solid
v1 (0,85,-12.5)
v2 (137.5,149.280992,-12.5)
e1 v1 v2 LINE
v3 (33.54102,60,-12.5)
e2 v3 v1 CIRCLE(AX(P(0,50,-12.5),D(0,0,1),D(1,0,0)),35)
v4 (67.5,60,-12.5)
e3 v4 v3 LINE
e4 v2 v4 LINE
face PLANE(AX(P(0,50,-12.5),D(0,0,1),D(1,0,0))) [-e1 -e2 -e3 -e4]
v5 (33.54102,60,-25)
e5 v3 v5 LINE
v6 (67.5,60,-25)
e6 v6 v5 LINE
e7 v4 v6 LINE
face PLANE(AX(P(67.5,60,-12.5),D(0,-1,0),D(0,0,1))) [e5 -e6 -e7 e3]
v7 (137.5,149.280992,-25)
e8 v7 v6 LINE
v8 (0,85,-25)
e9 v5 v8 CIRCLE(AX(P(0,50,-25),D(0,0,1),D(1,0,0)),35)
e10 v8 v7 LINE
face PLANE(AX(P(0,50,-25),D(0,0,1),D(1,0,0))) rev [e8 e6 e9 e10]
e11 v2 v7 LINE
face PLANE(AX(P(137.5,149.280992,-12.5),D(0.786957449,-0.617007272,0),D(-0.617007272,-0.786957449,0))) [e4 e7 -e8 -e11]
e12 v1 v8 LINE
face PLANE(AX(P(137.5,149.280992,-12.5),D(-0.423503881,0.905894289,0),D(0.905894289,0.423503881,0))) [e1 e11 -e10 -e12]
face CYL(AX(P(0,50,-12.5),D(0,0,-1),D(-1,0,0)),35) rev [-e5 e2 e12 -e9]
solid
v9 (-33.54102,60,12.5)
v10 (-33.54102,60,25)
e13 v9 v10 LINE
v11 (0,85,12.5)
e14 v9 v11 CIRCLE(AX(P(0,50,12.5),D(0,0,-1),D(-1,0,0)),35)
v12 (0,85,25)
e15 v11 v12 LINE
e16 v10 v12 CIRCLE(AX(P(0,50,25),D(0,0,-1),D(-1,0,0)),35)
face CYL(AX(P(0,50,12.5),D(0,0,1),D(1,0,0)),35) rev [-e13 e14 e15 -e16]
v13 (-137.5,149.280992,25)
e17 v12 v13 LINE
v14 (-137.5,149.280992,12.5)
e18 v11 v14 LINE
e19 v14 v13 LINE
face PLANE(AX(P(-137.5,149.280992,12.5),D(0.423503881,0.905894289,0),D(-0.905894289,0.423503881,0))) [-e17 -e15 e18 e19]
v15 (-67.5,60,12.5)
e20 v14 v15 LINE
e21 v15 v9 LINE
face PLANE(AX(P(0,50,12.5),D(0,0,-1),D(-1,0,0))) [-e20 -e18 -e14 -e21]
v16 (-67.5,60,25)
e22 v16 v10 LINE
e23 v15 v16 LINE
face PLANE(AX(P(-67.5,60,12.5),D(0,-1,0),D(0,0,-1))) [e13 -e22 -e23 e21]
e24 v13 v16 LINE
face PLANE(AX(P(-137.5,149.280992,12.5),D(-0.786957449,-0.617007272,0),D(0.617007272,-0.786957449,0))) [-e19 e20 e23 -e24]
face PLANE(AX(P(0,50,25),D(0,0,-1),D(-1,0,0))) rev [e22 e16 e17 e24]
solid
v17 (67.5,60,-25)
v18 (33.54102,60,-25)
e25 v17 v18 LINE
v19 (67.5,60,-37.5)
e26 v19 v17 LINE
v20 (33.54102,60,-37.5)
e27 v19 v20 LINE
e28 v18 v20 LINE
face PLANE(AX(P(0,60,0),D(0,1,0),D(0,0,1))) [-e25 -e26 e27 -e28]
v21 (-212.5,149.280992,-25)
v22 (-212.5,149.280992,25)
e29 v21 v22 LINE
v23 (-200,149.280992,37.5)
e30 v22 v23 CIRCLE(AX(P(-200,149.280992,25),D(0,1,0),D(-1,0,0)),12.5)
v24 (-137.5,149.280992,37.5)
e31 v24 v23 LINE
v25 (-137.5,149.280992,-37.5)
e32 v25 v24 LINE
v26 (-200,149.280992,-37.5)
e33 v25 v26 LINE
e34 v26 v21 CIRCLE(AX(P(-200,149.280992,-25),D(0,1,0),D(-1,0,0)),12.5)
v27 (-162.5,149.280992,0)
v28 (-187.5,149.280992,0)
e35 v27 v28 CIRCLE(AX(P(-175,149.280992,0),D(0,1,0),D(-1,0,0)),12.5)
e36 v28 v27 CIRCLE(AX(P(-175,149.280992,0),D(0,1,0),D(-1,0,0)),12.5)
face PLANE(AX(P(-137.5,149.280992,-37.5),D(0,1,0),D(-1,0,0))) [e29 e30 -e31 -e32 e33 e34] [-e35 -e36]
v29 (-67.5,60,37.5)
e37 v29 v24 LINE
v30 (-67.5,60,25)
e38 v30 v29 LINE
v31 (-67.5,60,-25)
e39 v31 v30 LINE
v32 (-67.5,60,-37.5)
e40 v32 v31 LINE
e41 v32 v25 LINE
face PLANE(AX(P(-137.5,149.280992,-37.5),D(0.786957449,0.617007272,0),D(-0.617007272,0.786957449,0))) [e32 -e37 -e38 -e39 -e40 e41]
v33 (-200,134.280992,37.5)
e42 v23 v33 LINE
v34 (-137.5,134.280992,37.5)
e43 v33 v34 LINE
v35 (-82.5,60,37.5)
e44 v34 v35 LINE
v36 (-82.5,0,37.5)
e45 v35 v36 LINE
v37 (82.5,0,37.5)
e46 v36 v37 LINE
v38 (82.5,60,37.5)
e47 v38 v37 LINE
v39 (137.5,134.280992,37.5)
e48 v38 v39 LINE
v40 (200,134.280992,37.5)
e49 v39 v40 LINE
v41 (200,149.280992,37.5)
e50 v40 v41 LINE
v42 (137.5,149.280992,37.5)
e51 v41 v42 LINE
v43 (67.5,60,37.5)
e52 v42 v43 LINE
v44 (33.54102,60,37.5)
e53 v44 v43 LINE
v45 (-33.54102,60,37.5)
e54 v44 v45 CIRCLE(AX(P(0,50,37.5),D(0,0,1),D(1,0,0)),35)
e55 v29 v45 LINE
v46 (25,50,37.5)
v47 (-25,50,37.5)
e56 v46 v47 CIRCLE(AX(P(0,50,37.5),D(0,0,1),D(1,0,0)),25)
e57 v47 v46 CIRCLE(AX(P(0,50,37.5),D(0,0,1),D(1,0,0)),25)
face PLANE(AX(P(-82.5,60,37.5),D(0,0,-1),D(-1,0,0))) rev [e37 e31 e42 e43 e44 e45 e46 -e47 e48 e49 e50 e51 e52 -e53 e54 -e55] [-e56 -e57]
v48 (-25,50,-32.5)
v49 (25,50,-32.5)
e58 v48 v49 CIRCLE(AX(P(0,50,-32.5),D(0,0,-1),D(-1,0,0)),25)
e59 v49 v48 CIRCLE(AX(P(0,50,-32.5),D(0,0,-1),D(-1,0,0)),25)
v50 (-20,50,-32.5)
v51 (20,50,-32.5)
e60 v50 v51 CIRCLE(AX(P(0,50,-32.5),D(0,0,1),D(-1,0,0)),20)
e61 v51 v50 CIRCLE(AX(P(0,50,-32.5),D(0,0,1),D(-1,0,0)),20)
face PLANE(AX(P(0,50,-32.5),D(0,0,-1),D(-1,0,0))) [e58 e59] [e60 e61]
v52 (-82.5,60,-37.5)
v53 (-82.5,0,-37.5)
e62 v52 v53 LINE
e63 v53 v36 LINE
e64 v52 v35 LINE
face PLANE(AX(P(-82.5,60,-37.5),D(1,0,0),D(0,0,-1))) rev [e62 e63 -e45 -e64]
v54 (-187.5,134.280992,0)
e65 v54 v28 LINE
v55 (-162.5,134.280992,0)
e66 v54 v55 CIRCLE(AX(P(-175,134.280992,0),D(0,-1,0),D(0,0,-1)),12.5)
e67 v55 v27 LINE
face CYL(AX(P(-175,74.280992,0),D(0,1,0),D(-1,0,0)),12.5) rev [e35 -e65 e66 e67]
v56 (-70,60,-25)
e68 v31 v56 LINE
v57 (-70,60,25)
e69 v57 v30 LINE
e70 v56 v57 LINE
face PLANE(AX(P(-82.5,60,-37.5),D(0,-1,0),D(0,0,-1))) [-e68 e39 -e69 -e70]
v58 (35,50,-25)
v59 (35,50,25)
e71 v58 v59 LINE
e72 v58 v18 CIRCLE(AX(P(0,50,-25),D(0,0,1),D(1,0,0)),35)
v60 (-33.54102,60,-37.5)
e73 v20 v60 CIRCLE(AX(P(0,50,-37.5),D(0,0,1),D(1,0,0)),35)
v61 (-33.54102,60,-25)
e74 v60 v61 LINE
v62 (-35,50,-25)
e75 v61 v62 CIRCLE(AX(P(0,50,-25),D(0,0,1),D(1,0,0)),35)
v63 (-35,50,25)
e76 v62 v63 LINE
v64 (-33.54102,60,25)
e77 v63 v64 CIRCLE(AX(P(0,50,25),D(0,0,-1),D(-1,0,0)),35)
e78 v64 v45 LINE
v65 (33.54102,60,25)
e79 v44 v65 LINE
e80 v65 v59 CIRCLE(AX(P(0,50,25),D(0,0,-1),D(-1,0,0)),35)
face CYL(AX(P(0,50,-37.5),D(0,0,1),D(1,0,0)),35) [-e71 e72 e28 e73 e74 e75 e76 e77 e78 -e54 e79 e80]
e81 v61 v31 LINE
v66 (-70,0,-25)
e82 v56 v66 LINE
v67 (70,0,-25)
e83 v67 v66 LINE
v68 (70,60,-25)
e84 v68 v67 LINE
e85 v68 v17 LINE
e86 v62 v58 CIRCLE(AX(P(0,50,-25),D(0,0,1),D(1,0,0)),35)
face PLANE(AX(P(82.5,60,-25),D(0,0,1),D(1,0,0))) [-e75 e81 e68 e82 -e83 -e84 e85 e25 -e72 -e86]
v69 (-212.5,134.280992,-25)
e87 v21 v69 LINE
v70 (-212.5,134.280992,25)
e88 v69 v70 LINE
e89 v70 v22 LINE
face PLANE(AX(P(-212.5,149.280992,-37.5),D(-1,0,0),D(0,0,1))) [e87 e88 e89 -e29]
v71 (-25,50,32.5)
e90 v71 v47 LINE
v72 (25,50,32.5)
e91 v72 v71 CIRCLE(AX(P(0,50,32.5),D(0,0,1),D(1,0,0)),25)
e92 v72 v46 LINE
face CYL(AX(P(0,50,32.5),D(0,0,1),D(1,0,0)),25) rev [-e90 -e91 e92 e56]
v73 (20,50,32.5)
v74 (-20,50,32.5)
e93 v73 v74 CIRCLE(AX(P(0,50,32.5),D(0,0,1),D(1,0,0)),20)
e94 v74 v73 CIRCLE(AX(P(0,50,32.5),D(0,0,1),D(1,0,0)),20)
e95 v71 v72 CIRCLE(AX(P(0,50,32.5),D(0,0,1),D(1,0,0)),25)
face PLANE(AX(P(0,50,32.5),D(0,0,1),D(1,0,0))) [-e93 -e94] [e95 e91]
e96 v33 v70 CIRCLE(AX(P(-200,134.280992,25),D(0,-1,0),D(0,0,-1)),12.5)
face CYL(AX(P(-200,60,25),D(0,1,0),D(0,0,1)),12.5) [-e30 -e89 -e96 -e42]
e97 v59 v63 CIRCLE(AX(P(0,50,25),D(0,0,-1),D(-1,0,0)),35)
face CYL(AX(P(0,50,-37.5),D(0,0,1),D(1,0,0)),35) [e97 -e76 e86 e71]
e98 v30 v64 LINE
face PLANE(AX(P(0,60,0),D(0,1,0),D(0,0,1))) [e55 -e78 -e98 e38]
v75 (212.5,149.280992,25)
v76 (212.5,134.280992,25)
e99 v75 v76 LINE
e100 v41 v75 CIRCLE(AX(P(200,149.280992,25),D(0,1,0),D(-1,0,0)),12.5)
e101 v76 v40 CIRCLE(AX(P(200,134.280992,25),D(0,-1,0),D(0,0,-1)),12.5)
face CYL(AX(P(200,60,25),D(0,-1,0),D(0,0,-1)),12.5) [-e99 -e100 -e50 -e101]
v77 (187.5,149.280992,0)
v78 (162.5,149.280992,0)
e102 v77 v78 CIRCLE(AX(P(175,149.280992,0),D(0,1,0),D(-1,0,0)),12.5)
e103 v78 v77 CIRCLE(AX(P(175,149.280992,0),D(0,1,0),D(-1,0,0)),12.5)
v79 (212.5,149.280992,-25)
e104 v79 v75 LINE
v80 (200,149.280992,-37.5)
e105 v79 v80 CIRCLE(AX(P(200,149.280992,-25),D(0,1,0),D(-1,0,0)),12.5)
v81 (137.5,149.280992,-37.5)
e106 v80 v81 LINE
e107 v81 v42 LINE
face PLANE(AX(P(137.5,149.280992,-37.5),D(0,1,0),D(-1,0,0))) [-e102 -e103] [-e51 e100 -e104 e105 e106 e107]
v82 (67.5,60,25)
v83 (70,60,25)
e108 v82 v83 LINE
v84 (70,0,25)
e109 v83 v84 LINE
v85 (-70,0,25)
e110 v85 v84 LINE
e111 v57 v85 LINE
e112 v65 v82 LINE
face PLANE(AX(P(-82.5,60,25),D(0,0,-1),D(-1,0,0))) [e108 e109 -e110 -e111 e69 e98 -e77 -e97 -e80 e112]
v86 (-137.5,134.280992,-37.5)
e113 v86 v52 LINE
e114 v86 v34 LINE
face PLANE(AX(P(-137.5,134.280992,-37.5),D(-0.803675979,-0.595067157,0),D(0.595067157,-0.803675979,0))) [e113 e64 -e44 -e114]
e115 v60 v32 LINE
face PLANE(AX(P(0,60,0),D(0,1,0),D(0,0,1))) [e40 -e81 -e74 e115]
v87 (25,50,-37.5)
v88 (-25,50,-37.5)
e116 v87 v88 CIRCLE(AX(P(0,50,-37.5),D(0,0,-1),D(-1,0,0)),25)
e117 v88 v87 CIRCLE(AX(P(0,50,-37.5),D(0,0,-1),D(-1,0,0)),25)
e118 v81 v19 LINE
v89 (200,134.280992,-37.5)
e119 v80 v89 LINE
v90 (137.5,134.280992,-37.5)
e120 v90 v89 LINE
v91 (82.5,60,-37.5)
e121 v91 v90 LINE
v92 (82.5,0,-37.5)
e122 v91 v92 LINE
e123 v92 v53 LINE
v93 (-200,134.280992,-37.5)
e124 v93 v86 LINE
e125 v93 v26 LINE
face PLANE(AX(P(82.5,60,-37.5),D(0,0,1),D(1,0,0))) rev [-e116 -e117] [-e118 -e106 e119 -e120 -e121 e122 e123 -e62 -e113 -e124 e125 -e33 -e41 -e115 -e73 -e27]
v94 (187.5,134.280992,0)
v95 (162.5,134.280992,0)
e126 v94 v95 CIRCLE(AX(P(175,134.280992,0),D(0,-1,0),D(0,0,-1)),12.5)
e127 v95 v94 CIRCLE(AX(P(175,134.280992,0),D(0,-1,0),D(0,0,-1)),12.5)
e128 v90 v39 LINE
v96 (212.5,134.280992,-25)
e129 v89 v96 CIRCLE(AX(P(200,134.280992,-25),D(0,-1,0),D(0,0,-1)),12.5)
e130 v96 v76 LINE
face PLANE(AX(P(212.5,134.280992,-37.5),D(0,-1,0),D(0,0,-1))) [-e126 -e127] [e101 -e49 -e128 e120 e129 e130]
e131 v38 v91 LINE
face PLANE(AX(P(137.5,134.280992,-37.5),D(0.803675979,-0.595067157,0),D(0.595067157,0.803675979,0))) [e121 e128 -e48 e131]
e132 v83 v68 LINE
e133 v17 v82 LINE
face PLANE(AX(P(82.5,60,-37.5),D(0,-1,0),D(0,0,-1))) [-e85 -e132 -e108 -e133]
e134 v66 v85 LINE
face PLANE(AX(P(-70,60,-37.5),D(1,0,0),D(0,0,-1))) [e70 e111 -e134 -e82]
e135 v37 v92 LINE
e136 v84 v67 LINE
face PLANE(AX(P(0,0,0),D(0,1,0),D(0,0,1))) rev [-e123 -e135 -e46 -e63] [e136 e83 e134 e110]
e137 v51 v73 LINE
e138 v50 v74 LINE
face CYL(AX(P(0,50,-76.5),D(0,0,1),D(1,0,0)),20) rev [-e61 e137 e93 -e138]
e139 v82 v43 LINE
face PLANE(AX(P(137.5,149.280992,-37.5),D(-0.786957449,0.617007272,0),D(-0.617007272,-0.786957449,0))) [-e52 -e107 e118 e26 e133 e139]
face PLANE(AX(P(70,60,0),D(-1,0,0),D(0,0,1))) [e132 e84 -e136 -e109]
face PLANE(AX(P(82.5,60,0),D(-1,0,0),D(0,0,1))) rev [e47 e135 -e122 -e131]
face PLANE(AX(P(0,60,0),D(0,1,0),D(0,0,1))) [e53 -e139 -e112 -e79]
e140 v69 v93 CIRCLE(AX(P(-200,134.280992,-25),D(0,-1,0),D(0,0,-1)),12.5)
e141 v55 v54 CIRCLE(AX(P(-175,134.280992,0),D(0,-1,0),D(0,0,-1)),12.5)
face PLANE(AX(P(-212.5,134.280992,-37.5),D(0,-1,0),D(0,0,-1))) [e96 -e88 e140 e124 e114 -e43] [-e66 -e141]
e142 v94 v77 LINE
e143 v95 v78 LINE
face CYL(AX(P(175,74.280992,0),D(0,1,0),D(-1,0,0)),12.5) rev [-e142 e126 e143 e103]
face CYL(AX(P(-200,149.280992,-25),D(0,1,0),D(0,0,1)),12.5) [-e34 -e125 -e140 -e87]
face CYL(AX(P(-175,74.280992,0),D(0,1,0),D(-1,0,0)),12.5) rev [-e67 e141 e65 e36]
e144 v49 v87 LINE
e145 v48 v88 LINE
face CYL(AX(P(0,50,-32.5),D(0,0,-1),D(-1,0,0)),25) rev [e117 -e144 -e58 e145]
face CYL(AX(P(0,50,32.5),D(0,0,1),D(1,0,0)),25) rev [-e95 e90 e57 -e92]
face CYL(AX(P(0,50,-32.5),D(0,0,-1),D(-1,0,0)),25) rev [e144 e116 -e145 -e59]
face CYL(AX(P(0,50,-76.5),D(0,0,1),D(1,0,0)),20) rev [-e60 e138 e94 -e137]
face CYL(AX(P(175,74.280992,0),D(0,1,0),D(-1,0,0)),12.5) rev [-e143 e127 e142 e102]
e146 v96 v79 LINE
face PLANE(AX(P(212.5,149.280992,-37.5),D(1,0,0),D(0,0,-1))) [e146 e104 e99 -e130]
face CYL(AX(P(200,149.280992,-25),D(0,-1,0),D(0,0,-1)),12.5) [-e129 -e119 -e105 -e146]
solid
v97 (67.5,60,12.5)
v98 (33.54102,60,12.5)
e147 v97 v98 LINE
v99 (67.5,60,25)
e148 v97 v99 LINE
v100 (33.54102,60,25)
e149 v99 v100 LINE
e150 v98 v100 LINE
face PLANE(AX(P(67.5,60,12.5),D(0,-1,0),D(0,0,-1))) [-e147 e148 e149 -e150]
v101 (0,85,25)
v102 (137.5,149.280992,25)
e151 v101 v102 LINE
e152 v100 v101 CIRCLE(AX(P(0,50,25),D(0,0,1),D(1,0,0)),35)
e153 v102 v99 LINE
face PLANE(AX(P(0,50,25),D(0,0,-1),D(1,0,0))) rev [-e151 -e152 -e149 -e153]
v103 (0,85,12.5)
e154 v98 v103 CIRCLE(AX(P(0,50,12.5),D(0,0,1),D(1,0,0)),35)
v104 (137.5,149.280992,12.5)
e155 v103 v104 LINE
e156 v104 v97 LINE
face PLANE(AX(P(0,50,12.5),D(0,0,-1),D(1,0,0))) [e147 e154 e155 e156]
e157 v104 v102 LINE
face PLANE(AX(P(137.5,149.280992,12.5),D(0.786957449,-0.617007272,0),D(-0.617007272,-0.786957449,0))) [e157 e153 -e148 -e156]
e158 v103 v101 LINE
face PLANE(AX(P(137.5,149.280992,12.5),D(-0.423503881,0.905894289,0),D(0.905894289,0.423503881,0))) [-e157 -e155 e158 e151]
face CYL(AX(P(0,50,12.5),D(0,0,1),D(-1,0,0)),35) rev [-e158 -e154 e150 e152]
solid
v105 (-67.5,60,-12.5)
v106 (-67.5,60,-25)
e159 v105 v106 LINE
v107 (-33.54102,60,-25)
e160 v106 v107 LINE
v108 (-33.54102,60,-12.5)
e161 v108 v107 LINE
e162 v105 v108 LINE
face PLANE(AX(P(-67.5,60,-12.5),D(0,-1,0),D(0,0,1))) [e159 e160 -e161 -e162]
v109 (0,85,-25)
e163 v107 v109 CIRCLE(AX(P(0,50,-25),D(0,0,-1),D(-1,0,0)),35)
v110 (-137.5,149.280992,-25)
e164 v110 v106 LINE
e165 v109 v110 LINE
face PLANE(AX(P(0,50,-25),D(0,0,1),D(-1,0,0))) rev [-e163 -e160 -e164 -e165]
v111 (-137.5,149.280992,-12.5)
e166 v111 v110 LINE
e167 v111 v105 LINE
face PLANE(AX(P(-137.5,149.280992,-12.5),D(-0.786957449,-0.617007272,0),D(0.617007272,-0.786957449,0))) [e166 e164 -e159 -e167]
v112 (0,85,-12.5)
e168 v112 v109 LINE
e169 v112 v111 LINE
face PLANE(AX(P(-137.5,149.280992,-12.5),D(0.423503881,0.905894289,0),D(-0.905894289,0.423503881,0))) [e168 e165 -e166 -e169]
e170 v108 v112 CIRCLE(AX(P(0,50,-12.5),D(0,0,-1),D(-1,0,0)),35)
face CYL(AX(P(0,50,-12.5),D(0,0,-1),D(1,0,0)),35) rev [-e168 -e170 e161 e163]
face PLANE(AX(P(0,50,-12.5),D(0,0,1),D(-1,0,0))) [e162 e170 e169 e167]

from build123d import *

# Parameters (mm, degrees)
BRACKET_BODY_THIN_60X12_5_DEPTH = 60
MOUNTING_FLANGE_PADS_DEPTH      = 75
FLANGE_HOLES_SKETCH_R           = 12.5
FLANGE_MOUNTING_HOLES_2X_DEPTH  = 75
FLANGE_CORNER_FILLET_R12_5_A_R  = 12.5
FLANGE_CORNER_FILLET_R12_5_B_R  = 12.5
BEARING_BOSS_SKETCH_R           = 35
BEARING_BOSS_DEPTH              = 75
BORE_RECESS_A_SKETCH_R          = 25
BORE_RECESS_A_5MM_DEPTH         = 5
BEARING_BORE_SKETCH_R           = 20
BEARING_BORE_DEPTH              = 109
BORE_START                      = -5
BORE_RECESS_B_SKETCH_R          = 25
BORE_RECESS_B_5MM_DEPTH         = 5
RIB_DEPTH                       = 12.5


with BuildPart() as part:
    # Bracket Profile Sketch → Bracket Body Thin 60x12.5 (new body)
    with BuildSketch(Plane(origin=(0, 0, 0), x_dir=(1, 0, 0), z_dir=(0, 1, 0))):
        Polygon((82.5, 0), (82.5, 37.5), (-82.5, 37.5), (-82.5, -37.5), (82.5, -37.5), align=None)
        Polygon((70, 0), (70, 25), (-70, 25), (-70, -25), (70, -25), align=None, mode=Mode.SUBTRACT)
    extrude(amount=BRACKET_BODY_THIN_60X12_5_DEPTH)

    # Flange Pads Sketch → Mounting Flange Pads (add)
    with BuildSketch(Plane.XY.offset(37.5)):
        Polygon((82.5, 60), (67.5, 60), (137.5, 149.280992191), (212.5, 149.280992191), (212.5, 134.280992191), (137.5, 134.280992191), align=None)
        Polygon((-137.5, 149.280992191), (-67.5, 60), (-82.5, 60), (-137.5, 134.280992191), (-212.5, 134.280992191), (-212.5, 149.280992191), align=None)
    extrude(amount=-MOUNTING_FLANGE_PADS_DEPTH)

    # Flange Holes Sketch → Flange Mounting Holes 2x (cut)
    with BuildSketch(Plane(origin=(0, 149.280992191, 0), x_dir=(1, 0, 0), z_dir=(0, 1, 0))):
        with Locations(Location((175, 0, 0), (0, 0, 180))):
            Circle(FLANGE_HOLES_SKETCH_R)
        with Locations(Location((-175, 0, 0), (0, 0, 180))):
            Circle(FLANGE_HOLES_SKETCH_R)
    extrude(amount=-FLANGE_MOUNTING_HOLES_2X_DEPTH, mode=Mode.SUBTRACT)

    # Flange Corner Fillet R12.5 A
    flange_corner_fillet_r12_5_a_edges = [part.edges().sort_by_distance(p)[0] for p in [
        (-212.5, 141.780992191, 37.5),
        (212.5, 141.780992191, 37.5),
    ]]
    fillet(flange_corner_fillet_r12_5_a_edges, radius=FLANGE_CORNER_FILLET_R12_5_A_R)

    # Flange Corner Fillet R12.5 B
    flange_corner_fillet_r12_5_b_edges = [part.edges().sort_by_distance(p)[0] for p in [
        (-212.5, 141.780992191, -37.5),
        (212.5, 141.780992191, -37.5),
    ]]
    fillet(flange_corner_fillet_r12_5_b_edges, radius=FLANGE_CORNER_FILLET_R12_5_B_R)

    # Bearing Boss Sketch → Bearing Boss (add)
    with BuildSketch(Plane.XY.offset(37.5)):
        with Locations(Location((0, 50, 0), (0, 0, 16.601549599))):
            Circle(BEARING_BOSS_SKETCH_R)
    extrude(amount=-BEARING_BOSS_DEPTH)

    # Bore Recess A Sketch → Bore Recess A 5mm (cut)
    with BuildSketch(Plane.XY.offset(37.5)):
        with Locations((0, 50)):
            Circle(BORE_RECESS_A_SKETCH_R)
    extrude(amount=-BORE_RECESS_A_5MM_DEPTH, mode=Mode.SUBTRACT)

    # Bearing Bore Sketch → Bearing Bore (cut)
    with BuildSketch(Plane.XY.offset(32.5)):
        with Locations((0, 50)):
            Circle(BEARING_BORE_SKETCH_R)
    extrude(amount=-BEARING_BORE_DEPTH, mode=Mode.SUBTRACT)

    # Bore Recess B Sketch → Bore Recess B 5mm (cut)
    with BuildSketch(Plane(origin=(0, 0, -37.5), x_dir=(-1, 0, 0), z_dir=(0, 0, -1)).offset(BORE_START)):
        with Locations(Location((0, 50, 0), (0, 0, 180))):
            Circle(BORE_RECESS_B_SKETCH_R)
    extrude(amount=BORE_RECESS_B_5MM_DEPTH, mode=Mode.SUBTRACT)


with BuildPart() as body_2:
    # Rib Sketch → Rib (new body)
    with BuildSketch(Plane.XY.offset(25)):
        with BuildLine():
            Line((-137.5, 149.280992191), (0, 85))
            ThreePointArc((0, 85), (-20.916500663, 78.062430401), (-33.541019662, 60))
            Line((-33.541019662, 60), (-67.5, 60))
            Line((-67.5, 60), (-137.5, 149.280992191))
        make_face()
    extrude(amount=-RIB_DEPTH)


with BuildPart() as body_3:
    # Rib Mirror Front Plane: mirrored copy
    add(body_2.part.mirror(Plane.XY))


with BuildPart() as body_4:
    # Rib Mirror Right Plane: mirrored copy
    add(body_3.part.mirror(Plane(origin=(0, 0, 0), x_dir=(0, 0, 1), z_dir=(1, 0, 0))))


with BuildPart() as body_5:
    # Rib Mirror Right Plane 2: mirrored copy
    add(body_2.part.mirror(Plane(origin=(0, 0, 0), x_dir=(0, 0, 1), z_dir=(1, 0, 0))))


solid = Compound([part.part, body_2.part, body_3.part, body_4.part, body_5.part])
